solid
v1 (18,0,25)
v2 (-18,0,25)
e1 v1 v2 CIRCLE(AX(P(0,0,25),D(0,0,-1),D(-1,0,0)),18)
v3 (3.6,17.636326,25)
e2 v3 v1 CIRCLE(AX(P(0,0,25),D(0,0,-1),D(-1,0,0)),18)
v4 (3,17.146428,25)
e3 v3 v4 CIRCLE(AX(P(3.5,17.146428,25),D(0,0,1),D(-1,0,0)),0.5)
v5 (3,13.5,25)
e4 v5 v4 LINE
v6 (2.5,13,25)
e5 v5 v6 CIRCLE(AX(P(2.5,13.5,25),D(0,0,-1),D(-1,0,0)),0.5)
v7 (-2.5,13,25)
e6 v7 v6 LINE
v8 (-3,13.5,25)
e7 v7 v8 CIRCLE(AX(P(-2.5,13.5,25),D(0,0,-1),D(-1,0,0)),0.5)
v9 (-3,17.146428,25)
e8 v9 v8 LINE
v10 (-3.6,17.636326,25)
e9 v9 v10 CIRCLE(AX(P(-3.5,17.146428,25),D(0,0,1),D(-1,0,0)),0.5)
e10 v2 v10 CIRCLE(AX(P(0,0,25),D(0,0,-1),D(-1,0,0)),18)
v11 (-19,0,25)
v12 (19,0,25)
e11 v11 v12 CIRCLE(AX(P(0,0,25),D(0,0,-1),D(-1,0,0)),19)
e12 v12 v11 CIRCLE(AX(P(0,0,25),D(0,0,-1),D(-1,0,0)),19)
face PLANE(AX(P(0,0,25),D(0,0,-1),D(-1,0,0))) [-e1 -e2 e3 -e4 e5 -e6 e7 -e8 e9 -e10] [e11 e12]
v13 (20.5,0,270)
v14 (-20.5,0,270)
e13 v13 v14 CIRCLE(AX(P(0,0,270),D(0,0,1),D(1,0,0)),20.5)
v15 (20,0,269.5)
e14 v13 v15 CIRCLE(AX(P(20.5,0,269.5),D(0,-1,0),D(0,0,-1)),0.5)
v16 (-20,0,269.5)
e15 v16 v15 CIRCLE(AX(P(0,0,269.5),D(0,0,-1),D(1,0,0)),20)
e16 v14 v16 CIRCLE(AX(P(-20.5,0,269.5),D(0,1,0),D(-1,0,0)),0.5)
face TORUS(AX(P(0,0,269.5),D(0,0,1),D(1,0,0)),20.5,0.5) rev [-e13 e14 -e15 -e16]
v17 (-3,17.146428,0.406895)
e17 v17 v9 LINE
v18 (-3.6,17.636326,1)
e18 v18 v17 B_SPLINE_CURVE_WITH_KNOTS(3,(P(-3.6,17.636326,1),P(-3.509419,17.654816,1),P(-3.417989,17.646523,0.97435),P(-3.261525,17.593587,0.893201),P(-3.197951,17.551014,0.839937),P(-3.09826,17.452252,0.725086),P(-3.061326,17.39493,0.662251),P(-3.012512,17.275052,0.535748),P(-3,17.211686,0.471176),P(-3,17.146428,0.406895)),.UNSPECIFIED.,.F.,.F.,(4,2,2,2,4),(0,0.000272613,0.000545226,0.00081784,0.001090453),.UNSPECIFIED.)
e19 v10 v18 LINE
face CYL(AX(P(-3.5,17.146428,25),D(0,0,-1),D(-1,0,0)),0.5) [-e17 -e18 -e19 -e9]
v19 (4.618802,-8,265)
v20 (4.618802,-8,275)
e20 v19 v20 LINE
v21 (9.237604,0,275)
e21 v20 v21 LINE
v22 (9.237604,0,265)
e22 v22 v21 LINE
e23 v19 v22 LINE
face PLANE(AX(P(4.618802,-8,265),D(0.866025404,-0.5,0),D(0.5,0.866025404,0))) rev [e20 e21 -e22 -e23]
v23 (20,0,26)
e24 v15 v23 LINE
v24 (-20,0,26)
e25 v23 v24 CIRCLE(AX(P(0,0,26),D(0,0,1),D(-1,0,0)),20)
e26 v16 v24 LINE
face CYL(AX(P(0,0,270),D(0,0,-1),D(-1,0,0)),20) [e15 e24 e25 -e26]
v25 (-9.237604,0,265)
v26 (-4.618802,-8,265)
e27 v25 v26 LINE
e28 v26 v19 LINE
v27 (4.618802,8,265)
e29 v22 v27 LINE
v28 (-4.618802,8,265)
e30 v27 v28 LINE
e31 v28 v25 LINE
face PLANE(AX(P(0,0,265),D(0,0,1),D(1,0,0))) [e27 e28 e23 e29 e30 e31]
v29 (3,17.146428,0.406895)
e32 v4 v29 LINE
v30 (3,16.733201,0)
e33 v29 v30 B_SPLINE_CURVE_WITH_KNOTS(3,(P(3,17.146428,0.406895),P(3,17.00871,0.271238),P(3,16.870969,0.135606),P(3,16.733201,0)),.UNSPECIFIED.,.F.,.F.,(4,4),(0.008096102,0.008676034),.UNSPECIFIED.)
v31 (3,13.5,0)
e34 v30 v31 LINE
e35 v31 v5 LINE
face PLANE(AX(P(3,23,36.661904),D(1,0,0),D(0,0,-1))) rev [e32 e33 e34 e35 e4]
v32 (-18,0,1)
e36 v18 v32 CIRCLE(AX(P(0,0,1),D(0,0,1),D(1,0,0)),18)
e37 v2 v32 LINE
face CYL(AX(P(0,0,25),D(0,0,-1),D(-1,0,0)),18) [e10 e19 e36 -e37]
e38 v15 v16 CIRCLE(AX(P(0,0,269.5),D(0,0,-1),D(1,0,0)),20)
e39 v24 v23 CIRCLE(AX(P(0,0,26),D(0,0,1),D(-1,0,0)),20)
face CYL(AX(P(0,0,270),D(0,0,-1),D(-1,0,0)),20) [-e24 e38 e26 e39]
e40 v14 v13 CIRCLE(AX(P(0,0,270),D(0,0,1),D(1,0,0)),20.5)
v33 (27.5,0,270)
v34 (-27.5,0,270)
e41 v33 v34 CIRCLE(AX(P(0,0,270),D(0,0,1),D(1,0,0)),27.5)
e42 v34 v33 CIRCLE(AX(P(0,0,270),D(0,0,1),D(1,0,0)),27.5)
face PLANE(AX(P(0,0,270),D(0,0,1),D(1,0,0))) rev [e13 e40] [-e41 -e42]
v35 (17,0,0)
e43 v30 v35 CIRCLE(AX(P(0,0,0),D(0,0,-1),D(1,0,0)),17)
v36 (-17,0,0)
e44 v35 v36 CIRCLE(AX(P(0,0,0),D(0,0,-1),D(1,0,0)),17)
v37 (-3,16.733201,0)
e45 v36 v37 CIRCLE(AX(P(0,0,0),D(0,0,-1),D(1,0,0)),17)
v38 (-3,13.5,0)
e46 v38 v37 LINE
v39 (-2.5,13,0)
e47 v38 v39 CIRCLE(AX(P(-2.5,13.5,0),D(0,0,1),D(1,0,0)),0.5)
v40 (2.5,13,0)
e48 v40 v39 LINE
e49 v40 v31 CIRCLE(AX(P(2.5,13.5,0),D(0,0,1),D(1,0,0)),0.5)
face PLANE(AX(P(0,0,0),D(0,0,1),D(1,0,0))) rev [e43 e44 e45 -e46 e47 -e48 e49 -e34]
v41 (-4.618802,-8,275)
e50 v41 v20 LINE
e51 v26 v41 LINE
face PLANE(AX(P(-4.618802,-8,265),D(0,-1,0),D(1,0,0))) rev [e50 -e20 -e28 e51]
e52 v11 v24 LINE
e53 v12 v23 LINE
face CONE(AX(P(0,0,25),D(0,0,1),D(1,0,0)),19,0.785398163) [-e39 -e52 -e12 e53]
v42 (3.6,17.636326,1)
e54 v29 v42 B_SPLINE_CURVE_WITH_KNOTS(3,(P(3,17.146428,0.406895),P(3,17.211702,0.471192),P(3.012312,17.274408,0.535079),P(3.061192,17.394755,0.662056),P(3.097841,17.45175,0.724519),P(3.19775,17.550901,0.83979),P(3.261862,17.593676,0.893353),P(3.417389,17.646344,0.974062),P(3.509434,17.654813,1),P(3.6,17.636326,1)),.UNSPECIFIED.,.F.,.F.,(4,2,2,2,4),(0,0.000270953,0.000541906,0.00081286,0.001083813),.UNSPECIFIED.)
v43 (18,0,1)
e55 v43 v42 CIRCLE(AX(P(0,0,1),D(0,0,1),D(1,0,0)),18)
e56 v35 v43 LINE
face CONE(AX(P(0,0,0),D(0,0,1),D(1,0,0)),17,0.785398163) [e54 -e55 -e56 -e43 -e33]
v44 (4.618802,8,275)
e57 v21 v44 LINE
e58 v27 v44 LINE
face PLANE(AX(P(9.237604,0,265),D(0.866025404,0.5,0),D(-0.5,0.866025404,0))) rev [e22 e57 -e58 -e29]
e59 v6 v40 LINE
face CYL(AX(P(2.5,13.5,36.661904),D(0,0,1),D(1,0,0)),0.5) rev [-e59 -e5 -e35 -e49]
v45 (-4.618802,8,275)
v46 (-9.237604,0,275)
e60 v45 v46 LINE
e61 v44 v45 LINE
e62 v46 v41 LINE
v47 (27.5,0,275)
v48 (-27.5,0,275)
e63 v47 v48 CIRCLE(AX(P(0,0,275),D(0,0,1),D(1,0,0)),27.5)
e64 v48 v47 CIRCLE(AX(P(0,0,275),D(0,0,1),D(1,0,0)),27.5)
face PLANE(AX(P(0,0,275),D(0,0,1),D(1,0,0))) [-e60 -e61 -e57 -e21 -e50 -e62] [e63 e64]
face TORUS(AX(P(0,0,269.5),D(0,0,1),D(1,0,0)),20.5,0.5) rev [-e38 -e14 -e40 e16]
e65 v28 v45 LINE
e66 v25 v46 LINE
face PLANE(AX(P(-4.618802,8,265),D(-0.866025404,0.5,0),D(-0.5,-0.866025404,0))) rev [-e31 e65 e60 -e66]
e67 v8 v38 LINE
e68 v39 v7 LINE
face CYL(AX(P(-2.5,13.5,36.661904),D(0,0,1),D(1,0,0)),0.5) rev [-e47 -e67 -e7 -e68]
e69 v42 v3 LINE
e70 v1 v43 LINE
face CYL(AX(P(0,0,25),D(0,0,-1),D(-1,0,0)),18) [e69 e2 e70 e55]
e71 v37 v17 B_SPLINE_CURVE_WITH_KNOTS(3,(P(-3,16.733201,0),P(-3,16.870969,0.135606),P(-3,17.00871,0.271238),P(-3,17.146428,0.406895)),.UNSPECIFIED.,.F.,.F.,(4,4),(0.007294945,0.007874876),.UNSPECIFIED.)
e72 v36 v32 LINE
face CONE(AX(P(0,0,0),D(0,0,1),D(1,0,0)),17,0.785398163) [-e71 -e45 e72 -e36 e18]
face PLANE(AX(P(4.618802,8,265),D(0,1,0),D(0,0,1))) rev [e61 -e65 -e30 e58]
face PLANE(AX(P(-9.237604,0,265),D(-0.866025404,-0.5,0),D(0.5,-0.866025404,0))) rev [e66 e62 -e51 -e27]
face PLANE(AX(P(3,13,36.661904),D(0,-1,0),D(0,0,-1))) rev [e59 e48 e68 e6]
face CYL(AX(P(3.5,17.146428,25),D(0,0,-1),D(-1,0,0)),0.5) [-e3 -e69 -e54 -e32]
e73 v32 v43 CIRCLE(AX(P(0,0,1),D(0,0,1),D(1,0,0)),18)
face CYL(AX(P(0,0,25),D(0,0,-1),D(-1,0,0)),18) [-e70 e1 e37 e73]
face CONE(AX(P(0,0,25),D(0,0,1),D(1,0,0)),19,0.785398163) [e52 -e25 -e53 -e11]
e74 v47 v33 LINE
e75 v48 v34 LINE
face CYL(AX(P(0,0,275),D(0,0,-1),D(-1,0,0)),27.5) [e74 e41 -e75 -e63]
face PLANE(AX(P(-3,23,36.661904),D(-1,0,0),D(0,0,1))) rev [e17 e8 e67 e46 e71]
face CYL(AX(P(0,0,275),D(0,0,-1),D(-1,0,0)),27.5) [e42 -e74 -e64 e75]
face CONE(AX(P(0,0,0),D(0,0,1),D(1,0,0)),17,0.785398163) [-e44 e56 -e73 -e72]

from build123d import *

# Parameters (mm, degrees)
SKETCH_1_R          = 20
EXTRUDE_1_DEPTH     = 270
SKETCH_2_R          = 27.5
EXTRUDE_2_DEPTH     = 5
CUT_EXTRUDE_1_DEPTH = 10
SKETCH_4_OUTSIDE_W  = 114.158
SKETCH_4_OUTSIDE_H  = 114.158
SKETCH_4_OUTSIDE_R  = 18
CUT_EXTRUDE_2_DEPTH = 25
CHAMFER_1_SIZE      = 1
CHAMFER_2_SIZE      = 1
FILLET_1_R          = 0.5
SKETCH_5_W          = 6
SKETCH_5_H          = 10
CUT_EXTRUDE_3_DEPTH = 25
FILLET_2_R          = 0.5


with BuildPart() as part:
    # 草图1 → 凸台-拉伸1 (new body)
    with BuildSketch(Plane.XY):
        Circle(SKETCH_1_R)
    extrude(amount=EXTRUDE_1_DEPTH)

    # 草图2 → 凸台-拉伸2 (add)
    with BuildSketch(Plane.XY.offset(270)):
        Circle(SKETCH_2_R)
    extrude(amount=EXTRUDE_2_DEPTH)

    # 草图3 → 切除-拉伸1 (cut)
    with BuildSketch(Plane.XY.offset(275)):
        Polygon((9.237604307, 0), (4.618802154, 8), (-4.618802154, 8), (-9.237604307, 0), (-4.618802154, -8), (4.618802154, -8), align=None)
    extrude(amount=-CUT_EXTRUDE_1_DEPTH, mode=Mode.SUBTRACT)

    # 草图4 outside → 切除-拉伸2 (cut)
    with BuildSketch(Plane(origin=(0, 0, 0), x_dir=(-1, 0, 0), z_dir=(0, 0, -1))):
        Rectangle(SKETCH_4_OUTSIDE_W, SKETCH_4_OUTSIDE_H)
        Circle(SKETCH_4_OUTSIDE_R, mode=Mode.SUBTRACT)
    extrude(amount=-CUT_EXTRUDE_2_DEPTH, mode=Mode.SUBTRACT)

    # 倒角1
    chamfer_1_edges = [part.edges().sort_by_distance(p)[0] for p in [
        (-20, 0, 25),
    ]]
    chamfer(chamfer_1_edges, length=CHAMFER_1_SIZE)

    # 倒角2
    chamfer_2_edges = [part.edges().sort_by_distance(p)[0] for p in [
        (18, 0, 0),
    ]]
    chamfer(chamfer_2_edges, length=CHAMFER_2_SIZE)

    # 圆角1
    fillet_1_edges = [part.edges().sort_by_distance(p)[0] for p in [
        (-20, 0, 270),
    ]]
    fillet(fillet_1_edges, radius=FILLET_1_R)

    # 草图5 → 切除-拉伸3 (cut)
    with BuildSketch(Plane(origin=(0, 0, 0), x_dir=(-1, 0, 0), z_dir=(0, 0, -1))):
        with Locations((0, 18)):
            Rectangle(SKETCH_5_W, SKETCH_5_H)
    extrude(amount=-CUT_EXTRUDE_3_DEPTH, mode=Mode.SUBTRACT)

    # 圆角2
    fillet_2_edges = [part.edges().sort_by_distance(p)[0] for p in [
        (3, 13, 12.5),
        (-3, 13, 12.5),
        (-3, 17.748239349, 13),
        (3, 17.748239349, 13),
    ]]
    fillet(fillet_2_edges, radius=FILLET_2_R)


solid = part.part
